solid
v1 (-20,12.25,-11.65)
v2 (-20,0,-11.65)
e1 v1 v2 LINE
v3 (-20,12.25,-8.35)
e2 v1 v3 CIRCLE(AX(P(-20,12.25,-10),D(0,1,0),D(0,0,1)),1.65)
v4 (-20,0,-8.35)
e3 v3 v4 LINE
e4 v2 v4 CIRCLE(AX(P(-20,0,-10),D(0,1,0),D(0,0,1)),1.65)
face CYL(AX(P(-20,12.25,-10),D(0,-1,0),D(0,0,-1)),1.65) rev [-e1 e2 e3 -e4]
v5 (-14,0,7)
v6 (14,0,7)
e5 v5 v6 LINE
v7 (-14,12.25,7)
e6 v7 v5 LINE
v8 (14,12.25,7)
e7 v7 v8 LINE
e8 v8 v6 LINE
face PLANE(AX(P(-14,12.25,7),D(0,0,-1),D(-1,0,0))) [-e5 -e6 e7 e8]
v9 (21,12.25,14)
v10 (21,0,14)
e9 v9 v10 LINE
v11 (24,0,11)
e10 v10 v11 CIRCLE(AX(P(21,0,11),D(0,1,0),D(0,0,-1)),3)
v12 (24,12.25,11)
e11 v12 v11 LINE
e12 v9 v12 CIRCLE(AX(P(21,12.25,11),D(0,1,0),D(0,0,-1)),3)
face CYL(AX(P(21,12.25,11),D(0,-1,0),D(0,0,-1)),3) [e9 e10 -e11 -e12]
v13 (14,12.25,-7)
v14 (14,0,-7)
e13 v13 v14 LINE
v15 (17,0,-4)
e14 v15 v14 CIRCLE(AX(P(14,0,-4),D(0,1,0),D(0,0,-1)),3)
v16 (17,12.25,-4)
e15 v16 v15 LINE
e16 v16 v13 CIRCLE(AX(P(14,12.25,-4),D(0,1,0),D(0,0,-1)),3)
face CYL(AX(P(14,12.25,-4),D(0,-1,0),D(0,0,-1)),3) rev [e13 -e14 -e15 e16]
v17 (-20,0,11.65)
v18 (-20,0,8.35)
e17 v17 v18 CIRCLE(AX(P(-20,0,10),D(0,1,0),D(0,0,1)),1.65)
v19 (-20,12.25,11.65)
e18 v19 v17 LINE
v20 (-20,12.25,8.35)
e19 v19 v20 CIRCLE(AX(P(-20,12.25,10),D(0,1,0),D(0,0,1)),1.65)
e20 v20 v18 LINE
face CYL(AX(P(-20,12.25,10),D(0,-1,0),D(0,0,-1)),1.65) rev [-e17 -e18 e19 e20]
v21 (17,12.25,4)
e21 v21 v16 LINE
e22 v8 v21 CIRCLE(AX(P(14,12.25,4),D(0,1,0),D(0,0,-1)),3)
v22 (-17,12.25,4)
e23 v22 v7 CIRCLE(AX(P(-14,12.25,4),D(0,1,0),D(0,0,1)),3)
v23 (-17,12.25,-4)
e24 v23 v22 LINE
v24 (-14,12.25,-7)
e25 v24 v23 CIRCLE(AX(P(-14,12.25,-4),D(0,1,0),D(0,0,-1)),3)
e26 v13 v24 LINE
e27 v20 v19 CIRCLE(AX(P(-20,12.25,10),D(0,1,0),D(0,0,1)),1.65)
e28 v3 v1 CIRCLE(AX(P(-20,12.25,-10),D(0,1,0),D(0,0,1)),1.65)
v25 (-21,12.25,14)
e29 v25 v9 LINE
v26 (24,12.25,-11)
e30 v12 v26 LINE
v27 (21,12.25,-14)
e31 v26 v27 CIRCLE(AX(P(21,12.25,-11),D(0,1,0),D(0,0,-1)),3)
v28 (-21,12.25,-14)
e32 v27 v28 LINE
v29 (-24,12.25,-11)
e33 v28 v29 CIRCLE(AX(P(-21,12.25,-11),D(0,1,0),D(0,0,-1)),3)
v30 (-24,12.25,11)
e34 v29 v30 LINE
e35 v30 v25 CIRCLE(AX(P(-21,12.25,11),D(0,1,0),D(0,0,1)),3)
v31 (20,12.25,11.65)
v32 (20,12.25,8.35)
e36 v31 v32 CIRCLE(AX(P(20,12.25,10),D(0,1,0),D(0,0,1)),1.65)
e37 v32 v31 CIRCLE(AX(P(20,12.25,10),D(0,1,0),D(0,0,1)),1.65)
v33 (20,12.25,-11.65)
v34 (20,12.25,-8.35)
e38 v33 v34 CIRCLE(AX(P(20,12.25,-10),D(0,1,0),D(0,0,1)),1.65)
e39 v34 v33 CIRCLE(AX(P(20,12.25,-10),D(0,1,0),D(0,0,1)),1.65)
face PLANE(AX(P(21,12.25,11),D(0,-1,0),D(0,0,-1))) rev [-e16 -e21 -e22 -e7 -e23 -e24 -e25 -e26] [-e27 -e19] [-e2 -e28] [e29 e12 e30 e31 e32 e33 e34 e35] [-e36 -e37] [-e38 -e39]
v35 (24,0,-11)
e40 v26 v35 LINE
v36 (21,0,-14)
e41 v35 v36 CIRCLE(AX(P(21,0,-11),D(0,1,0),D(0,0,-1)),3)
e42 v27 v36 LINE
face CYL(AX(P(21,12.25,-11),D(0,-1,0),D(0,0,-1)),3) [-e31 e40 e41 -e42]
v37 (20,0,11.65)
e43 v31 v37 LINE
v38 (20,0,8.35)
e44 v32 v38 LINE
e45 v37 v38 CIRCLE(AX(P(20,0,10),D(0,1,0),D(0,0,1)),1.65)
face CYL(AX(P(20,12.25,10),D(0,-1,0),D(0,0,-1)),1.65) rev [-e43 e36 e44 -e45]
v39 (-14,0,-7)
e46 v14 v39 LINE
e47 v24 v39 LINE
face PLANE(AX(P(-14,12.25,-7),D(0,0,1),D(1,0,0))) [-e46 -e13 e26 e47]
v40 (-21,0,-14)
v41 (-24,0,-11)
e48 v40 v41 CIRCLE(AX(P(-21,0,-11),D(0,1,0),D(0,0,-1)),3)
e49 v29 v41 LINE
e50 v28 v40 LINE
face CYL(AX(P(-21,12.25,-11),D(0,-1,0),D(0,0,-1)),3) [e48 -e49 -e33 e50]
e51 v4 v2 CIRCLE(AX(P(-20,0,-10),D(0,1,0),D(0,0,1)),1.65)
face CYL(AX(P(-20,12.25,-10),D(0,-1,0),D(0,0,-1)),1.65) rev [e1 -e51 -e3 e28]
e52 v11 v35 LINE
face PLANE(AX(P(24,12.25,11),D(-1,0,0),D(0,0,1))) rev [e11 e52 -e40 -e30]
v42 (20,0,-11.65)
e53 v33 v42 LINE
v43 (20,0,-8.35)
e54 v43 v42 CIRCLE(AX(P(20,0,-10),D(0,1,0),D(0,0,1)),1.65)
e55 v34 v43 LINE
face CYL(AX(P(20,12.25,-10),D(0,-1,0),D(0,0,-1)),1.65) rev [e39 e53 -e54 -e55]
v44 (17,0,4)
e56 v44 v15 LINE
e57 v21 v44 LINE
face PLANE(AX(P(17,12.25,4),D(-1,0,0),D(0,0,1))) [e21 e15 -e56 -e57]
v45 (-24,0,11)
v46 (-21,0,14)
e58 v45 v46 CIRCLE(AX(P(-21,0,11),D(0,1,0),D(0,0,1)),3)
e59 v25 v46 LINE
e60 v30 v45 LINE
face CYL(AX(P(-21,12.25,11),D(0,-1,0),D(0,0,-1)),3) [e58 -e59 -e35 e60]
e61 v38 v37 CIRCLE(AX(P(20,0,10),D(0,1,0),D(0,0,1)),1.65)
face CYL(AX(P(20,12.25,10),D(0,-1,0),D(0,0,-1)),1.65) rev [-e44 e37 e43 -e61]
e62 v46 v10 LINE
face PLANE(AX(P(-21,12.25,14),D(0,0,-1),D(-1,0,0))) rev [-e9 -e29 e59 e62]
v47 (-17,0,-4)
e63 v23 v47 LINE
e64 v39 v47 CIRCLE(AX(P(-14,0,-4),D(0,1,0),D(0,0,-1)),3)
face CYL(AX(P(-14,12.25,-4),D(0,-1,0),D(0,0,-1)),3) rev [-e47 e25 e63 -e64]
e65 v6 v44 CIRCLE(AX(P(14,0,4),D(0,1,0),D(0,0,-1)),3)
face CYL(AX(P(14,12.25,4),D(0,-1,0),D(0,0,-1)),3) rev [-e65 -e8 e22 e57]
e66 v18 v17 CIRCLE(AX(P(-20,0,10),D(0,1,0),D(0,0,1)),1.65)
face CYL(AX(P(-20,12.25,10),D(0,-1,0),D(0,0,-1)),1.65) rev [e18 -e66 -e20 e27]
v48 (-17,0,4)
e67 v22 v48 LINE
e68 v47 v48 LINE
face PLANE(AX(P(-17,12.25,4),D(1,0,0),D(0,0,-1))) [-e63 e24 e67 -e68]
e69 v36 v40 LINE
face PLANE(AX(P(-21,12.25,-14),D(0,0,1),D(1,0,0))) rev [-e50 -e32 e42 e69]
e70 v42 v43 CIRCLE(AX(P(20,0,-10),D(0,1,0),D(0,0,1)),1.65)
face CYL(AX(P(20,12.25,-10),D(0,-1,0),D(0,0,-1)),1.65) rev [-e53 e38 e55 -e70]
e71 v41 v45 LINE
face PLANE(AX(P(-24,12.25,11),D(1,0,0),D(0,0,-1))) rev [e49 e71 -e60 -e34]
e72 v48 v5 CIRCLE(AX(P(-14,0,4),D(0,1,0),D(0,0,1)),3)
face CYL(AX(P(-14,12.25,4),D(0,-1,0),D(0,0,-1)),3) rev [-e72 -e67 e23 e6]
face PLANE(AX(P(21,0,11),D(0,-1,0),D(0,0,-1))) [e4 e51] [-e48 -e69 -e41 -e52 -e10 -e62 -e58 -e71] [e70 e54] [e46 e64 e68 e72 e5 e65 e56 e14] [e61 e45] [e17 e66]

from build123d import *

# Parameters (mm, degrees)
SKETCH_1_R      = 1.65
EXTRUDE_1_DEPTH = 12.25


with BuildPart() as part:
    # 草图1 → 凸台-拉伸1 (new body)
    with BuildSketch(Plane(origin=(0, 0, 0), x_dir=(1, 0, 0), z_dir=(0, 1, 0))):
        with BuildLine():
            Line((-24, -11), (-24, 11))
            ThreePointArc((-24, 11), (-23.121320344, 13.121320344), (-21, 14))
            Line((-21, 14), (21, 14))
            ThreePointArc((21, 14), (23.121320344, 13.121320344), (24, 11))
            Line((24, 11), (24, -11))
            ThreePointArc((24, -11), (23.121320344, -13.121320344), (21, -14))
            Line((21, -14), (-21, -14))
            ThreePointArc((-21, -14), (-23.121320344, -13.121320344), (-24, -11))
        make_face()
        with Locations(Location((-20, 10, 0), (0, 0, 270))):
            Circle(SKETCH_1_R, mode=Mode.SUBTRACT)
        with Locations(Location((-20, -10, 0), (0, 0, 270))):
            Circle(SKETCH_1_R, mode=Mode.SUBTRACT)
        with Locations(Location((20, -10, 0), (0, 0, 270))):
            Circle(SKETCH_1_R, mode=Mode.SUBTRACT)
        with Locations(Location((20, 10, 0), (0, 0, 270))):
            Circle(SKETCH_1_R, mode=Mode.SUBTRACT)
        with BuildLine():
            Line((-17, -4), (-17, 4))
            ThreePointArc((-17, 4), (-16.121320344, 6.121320344), (-14, 7))
            Line((-14, 7), (14, 7))
            ThreePointArc((14, 7), (16.121320344, 6.121320344), (17, 4))
            Line((17, 4), (17, -4))
            ThreePointArc((17, -4), (16.121320344, -6.121320344), (14, -7))
            Line((14, -7), (-14, -7))
            ThreePointArc((-14, -7), (-16.121320344, -6.121320344), (-17, -4))
        make_face(mode=Mode.SUBTRACT)
    extrude(amount=EXTRUDE_1_DEPTH)


solid = part.part
